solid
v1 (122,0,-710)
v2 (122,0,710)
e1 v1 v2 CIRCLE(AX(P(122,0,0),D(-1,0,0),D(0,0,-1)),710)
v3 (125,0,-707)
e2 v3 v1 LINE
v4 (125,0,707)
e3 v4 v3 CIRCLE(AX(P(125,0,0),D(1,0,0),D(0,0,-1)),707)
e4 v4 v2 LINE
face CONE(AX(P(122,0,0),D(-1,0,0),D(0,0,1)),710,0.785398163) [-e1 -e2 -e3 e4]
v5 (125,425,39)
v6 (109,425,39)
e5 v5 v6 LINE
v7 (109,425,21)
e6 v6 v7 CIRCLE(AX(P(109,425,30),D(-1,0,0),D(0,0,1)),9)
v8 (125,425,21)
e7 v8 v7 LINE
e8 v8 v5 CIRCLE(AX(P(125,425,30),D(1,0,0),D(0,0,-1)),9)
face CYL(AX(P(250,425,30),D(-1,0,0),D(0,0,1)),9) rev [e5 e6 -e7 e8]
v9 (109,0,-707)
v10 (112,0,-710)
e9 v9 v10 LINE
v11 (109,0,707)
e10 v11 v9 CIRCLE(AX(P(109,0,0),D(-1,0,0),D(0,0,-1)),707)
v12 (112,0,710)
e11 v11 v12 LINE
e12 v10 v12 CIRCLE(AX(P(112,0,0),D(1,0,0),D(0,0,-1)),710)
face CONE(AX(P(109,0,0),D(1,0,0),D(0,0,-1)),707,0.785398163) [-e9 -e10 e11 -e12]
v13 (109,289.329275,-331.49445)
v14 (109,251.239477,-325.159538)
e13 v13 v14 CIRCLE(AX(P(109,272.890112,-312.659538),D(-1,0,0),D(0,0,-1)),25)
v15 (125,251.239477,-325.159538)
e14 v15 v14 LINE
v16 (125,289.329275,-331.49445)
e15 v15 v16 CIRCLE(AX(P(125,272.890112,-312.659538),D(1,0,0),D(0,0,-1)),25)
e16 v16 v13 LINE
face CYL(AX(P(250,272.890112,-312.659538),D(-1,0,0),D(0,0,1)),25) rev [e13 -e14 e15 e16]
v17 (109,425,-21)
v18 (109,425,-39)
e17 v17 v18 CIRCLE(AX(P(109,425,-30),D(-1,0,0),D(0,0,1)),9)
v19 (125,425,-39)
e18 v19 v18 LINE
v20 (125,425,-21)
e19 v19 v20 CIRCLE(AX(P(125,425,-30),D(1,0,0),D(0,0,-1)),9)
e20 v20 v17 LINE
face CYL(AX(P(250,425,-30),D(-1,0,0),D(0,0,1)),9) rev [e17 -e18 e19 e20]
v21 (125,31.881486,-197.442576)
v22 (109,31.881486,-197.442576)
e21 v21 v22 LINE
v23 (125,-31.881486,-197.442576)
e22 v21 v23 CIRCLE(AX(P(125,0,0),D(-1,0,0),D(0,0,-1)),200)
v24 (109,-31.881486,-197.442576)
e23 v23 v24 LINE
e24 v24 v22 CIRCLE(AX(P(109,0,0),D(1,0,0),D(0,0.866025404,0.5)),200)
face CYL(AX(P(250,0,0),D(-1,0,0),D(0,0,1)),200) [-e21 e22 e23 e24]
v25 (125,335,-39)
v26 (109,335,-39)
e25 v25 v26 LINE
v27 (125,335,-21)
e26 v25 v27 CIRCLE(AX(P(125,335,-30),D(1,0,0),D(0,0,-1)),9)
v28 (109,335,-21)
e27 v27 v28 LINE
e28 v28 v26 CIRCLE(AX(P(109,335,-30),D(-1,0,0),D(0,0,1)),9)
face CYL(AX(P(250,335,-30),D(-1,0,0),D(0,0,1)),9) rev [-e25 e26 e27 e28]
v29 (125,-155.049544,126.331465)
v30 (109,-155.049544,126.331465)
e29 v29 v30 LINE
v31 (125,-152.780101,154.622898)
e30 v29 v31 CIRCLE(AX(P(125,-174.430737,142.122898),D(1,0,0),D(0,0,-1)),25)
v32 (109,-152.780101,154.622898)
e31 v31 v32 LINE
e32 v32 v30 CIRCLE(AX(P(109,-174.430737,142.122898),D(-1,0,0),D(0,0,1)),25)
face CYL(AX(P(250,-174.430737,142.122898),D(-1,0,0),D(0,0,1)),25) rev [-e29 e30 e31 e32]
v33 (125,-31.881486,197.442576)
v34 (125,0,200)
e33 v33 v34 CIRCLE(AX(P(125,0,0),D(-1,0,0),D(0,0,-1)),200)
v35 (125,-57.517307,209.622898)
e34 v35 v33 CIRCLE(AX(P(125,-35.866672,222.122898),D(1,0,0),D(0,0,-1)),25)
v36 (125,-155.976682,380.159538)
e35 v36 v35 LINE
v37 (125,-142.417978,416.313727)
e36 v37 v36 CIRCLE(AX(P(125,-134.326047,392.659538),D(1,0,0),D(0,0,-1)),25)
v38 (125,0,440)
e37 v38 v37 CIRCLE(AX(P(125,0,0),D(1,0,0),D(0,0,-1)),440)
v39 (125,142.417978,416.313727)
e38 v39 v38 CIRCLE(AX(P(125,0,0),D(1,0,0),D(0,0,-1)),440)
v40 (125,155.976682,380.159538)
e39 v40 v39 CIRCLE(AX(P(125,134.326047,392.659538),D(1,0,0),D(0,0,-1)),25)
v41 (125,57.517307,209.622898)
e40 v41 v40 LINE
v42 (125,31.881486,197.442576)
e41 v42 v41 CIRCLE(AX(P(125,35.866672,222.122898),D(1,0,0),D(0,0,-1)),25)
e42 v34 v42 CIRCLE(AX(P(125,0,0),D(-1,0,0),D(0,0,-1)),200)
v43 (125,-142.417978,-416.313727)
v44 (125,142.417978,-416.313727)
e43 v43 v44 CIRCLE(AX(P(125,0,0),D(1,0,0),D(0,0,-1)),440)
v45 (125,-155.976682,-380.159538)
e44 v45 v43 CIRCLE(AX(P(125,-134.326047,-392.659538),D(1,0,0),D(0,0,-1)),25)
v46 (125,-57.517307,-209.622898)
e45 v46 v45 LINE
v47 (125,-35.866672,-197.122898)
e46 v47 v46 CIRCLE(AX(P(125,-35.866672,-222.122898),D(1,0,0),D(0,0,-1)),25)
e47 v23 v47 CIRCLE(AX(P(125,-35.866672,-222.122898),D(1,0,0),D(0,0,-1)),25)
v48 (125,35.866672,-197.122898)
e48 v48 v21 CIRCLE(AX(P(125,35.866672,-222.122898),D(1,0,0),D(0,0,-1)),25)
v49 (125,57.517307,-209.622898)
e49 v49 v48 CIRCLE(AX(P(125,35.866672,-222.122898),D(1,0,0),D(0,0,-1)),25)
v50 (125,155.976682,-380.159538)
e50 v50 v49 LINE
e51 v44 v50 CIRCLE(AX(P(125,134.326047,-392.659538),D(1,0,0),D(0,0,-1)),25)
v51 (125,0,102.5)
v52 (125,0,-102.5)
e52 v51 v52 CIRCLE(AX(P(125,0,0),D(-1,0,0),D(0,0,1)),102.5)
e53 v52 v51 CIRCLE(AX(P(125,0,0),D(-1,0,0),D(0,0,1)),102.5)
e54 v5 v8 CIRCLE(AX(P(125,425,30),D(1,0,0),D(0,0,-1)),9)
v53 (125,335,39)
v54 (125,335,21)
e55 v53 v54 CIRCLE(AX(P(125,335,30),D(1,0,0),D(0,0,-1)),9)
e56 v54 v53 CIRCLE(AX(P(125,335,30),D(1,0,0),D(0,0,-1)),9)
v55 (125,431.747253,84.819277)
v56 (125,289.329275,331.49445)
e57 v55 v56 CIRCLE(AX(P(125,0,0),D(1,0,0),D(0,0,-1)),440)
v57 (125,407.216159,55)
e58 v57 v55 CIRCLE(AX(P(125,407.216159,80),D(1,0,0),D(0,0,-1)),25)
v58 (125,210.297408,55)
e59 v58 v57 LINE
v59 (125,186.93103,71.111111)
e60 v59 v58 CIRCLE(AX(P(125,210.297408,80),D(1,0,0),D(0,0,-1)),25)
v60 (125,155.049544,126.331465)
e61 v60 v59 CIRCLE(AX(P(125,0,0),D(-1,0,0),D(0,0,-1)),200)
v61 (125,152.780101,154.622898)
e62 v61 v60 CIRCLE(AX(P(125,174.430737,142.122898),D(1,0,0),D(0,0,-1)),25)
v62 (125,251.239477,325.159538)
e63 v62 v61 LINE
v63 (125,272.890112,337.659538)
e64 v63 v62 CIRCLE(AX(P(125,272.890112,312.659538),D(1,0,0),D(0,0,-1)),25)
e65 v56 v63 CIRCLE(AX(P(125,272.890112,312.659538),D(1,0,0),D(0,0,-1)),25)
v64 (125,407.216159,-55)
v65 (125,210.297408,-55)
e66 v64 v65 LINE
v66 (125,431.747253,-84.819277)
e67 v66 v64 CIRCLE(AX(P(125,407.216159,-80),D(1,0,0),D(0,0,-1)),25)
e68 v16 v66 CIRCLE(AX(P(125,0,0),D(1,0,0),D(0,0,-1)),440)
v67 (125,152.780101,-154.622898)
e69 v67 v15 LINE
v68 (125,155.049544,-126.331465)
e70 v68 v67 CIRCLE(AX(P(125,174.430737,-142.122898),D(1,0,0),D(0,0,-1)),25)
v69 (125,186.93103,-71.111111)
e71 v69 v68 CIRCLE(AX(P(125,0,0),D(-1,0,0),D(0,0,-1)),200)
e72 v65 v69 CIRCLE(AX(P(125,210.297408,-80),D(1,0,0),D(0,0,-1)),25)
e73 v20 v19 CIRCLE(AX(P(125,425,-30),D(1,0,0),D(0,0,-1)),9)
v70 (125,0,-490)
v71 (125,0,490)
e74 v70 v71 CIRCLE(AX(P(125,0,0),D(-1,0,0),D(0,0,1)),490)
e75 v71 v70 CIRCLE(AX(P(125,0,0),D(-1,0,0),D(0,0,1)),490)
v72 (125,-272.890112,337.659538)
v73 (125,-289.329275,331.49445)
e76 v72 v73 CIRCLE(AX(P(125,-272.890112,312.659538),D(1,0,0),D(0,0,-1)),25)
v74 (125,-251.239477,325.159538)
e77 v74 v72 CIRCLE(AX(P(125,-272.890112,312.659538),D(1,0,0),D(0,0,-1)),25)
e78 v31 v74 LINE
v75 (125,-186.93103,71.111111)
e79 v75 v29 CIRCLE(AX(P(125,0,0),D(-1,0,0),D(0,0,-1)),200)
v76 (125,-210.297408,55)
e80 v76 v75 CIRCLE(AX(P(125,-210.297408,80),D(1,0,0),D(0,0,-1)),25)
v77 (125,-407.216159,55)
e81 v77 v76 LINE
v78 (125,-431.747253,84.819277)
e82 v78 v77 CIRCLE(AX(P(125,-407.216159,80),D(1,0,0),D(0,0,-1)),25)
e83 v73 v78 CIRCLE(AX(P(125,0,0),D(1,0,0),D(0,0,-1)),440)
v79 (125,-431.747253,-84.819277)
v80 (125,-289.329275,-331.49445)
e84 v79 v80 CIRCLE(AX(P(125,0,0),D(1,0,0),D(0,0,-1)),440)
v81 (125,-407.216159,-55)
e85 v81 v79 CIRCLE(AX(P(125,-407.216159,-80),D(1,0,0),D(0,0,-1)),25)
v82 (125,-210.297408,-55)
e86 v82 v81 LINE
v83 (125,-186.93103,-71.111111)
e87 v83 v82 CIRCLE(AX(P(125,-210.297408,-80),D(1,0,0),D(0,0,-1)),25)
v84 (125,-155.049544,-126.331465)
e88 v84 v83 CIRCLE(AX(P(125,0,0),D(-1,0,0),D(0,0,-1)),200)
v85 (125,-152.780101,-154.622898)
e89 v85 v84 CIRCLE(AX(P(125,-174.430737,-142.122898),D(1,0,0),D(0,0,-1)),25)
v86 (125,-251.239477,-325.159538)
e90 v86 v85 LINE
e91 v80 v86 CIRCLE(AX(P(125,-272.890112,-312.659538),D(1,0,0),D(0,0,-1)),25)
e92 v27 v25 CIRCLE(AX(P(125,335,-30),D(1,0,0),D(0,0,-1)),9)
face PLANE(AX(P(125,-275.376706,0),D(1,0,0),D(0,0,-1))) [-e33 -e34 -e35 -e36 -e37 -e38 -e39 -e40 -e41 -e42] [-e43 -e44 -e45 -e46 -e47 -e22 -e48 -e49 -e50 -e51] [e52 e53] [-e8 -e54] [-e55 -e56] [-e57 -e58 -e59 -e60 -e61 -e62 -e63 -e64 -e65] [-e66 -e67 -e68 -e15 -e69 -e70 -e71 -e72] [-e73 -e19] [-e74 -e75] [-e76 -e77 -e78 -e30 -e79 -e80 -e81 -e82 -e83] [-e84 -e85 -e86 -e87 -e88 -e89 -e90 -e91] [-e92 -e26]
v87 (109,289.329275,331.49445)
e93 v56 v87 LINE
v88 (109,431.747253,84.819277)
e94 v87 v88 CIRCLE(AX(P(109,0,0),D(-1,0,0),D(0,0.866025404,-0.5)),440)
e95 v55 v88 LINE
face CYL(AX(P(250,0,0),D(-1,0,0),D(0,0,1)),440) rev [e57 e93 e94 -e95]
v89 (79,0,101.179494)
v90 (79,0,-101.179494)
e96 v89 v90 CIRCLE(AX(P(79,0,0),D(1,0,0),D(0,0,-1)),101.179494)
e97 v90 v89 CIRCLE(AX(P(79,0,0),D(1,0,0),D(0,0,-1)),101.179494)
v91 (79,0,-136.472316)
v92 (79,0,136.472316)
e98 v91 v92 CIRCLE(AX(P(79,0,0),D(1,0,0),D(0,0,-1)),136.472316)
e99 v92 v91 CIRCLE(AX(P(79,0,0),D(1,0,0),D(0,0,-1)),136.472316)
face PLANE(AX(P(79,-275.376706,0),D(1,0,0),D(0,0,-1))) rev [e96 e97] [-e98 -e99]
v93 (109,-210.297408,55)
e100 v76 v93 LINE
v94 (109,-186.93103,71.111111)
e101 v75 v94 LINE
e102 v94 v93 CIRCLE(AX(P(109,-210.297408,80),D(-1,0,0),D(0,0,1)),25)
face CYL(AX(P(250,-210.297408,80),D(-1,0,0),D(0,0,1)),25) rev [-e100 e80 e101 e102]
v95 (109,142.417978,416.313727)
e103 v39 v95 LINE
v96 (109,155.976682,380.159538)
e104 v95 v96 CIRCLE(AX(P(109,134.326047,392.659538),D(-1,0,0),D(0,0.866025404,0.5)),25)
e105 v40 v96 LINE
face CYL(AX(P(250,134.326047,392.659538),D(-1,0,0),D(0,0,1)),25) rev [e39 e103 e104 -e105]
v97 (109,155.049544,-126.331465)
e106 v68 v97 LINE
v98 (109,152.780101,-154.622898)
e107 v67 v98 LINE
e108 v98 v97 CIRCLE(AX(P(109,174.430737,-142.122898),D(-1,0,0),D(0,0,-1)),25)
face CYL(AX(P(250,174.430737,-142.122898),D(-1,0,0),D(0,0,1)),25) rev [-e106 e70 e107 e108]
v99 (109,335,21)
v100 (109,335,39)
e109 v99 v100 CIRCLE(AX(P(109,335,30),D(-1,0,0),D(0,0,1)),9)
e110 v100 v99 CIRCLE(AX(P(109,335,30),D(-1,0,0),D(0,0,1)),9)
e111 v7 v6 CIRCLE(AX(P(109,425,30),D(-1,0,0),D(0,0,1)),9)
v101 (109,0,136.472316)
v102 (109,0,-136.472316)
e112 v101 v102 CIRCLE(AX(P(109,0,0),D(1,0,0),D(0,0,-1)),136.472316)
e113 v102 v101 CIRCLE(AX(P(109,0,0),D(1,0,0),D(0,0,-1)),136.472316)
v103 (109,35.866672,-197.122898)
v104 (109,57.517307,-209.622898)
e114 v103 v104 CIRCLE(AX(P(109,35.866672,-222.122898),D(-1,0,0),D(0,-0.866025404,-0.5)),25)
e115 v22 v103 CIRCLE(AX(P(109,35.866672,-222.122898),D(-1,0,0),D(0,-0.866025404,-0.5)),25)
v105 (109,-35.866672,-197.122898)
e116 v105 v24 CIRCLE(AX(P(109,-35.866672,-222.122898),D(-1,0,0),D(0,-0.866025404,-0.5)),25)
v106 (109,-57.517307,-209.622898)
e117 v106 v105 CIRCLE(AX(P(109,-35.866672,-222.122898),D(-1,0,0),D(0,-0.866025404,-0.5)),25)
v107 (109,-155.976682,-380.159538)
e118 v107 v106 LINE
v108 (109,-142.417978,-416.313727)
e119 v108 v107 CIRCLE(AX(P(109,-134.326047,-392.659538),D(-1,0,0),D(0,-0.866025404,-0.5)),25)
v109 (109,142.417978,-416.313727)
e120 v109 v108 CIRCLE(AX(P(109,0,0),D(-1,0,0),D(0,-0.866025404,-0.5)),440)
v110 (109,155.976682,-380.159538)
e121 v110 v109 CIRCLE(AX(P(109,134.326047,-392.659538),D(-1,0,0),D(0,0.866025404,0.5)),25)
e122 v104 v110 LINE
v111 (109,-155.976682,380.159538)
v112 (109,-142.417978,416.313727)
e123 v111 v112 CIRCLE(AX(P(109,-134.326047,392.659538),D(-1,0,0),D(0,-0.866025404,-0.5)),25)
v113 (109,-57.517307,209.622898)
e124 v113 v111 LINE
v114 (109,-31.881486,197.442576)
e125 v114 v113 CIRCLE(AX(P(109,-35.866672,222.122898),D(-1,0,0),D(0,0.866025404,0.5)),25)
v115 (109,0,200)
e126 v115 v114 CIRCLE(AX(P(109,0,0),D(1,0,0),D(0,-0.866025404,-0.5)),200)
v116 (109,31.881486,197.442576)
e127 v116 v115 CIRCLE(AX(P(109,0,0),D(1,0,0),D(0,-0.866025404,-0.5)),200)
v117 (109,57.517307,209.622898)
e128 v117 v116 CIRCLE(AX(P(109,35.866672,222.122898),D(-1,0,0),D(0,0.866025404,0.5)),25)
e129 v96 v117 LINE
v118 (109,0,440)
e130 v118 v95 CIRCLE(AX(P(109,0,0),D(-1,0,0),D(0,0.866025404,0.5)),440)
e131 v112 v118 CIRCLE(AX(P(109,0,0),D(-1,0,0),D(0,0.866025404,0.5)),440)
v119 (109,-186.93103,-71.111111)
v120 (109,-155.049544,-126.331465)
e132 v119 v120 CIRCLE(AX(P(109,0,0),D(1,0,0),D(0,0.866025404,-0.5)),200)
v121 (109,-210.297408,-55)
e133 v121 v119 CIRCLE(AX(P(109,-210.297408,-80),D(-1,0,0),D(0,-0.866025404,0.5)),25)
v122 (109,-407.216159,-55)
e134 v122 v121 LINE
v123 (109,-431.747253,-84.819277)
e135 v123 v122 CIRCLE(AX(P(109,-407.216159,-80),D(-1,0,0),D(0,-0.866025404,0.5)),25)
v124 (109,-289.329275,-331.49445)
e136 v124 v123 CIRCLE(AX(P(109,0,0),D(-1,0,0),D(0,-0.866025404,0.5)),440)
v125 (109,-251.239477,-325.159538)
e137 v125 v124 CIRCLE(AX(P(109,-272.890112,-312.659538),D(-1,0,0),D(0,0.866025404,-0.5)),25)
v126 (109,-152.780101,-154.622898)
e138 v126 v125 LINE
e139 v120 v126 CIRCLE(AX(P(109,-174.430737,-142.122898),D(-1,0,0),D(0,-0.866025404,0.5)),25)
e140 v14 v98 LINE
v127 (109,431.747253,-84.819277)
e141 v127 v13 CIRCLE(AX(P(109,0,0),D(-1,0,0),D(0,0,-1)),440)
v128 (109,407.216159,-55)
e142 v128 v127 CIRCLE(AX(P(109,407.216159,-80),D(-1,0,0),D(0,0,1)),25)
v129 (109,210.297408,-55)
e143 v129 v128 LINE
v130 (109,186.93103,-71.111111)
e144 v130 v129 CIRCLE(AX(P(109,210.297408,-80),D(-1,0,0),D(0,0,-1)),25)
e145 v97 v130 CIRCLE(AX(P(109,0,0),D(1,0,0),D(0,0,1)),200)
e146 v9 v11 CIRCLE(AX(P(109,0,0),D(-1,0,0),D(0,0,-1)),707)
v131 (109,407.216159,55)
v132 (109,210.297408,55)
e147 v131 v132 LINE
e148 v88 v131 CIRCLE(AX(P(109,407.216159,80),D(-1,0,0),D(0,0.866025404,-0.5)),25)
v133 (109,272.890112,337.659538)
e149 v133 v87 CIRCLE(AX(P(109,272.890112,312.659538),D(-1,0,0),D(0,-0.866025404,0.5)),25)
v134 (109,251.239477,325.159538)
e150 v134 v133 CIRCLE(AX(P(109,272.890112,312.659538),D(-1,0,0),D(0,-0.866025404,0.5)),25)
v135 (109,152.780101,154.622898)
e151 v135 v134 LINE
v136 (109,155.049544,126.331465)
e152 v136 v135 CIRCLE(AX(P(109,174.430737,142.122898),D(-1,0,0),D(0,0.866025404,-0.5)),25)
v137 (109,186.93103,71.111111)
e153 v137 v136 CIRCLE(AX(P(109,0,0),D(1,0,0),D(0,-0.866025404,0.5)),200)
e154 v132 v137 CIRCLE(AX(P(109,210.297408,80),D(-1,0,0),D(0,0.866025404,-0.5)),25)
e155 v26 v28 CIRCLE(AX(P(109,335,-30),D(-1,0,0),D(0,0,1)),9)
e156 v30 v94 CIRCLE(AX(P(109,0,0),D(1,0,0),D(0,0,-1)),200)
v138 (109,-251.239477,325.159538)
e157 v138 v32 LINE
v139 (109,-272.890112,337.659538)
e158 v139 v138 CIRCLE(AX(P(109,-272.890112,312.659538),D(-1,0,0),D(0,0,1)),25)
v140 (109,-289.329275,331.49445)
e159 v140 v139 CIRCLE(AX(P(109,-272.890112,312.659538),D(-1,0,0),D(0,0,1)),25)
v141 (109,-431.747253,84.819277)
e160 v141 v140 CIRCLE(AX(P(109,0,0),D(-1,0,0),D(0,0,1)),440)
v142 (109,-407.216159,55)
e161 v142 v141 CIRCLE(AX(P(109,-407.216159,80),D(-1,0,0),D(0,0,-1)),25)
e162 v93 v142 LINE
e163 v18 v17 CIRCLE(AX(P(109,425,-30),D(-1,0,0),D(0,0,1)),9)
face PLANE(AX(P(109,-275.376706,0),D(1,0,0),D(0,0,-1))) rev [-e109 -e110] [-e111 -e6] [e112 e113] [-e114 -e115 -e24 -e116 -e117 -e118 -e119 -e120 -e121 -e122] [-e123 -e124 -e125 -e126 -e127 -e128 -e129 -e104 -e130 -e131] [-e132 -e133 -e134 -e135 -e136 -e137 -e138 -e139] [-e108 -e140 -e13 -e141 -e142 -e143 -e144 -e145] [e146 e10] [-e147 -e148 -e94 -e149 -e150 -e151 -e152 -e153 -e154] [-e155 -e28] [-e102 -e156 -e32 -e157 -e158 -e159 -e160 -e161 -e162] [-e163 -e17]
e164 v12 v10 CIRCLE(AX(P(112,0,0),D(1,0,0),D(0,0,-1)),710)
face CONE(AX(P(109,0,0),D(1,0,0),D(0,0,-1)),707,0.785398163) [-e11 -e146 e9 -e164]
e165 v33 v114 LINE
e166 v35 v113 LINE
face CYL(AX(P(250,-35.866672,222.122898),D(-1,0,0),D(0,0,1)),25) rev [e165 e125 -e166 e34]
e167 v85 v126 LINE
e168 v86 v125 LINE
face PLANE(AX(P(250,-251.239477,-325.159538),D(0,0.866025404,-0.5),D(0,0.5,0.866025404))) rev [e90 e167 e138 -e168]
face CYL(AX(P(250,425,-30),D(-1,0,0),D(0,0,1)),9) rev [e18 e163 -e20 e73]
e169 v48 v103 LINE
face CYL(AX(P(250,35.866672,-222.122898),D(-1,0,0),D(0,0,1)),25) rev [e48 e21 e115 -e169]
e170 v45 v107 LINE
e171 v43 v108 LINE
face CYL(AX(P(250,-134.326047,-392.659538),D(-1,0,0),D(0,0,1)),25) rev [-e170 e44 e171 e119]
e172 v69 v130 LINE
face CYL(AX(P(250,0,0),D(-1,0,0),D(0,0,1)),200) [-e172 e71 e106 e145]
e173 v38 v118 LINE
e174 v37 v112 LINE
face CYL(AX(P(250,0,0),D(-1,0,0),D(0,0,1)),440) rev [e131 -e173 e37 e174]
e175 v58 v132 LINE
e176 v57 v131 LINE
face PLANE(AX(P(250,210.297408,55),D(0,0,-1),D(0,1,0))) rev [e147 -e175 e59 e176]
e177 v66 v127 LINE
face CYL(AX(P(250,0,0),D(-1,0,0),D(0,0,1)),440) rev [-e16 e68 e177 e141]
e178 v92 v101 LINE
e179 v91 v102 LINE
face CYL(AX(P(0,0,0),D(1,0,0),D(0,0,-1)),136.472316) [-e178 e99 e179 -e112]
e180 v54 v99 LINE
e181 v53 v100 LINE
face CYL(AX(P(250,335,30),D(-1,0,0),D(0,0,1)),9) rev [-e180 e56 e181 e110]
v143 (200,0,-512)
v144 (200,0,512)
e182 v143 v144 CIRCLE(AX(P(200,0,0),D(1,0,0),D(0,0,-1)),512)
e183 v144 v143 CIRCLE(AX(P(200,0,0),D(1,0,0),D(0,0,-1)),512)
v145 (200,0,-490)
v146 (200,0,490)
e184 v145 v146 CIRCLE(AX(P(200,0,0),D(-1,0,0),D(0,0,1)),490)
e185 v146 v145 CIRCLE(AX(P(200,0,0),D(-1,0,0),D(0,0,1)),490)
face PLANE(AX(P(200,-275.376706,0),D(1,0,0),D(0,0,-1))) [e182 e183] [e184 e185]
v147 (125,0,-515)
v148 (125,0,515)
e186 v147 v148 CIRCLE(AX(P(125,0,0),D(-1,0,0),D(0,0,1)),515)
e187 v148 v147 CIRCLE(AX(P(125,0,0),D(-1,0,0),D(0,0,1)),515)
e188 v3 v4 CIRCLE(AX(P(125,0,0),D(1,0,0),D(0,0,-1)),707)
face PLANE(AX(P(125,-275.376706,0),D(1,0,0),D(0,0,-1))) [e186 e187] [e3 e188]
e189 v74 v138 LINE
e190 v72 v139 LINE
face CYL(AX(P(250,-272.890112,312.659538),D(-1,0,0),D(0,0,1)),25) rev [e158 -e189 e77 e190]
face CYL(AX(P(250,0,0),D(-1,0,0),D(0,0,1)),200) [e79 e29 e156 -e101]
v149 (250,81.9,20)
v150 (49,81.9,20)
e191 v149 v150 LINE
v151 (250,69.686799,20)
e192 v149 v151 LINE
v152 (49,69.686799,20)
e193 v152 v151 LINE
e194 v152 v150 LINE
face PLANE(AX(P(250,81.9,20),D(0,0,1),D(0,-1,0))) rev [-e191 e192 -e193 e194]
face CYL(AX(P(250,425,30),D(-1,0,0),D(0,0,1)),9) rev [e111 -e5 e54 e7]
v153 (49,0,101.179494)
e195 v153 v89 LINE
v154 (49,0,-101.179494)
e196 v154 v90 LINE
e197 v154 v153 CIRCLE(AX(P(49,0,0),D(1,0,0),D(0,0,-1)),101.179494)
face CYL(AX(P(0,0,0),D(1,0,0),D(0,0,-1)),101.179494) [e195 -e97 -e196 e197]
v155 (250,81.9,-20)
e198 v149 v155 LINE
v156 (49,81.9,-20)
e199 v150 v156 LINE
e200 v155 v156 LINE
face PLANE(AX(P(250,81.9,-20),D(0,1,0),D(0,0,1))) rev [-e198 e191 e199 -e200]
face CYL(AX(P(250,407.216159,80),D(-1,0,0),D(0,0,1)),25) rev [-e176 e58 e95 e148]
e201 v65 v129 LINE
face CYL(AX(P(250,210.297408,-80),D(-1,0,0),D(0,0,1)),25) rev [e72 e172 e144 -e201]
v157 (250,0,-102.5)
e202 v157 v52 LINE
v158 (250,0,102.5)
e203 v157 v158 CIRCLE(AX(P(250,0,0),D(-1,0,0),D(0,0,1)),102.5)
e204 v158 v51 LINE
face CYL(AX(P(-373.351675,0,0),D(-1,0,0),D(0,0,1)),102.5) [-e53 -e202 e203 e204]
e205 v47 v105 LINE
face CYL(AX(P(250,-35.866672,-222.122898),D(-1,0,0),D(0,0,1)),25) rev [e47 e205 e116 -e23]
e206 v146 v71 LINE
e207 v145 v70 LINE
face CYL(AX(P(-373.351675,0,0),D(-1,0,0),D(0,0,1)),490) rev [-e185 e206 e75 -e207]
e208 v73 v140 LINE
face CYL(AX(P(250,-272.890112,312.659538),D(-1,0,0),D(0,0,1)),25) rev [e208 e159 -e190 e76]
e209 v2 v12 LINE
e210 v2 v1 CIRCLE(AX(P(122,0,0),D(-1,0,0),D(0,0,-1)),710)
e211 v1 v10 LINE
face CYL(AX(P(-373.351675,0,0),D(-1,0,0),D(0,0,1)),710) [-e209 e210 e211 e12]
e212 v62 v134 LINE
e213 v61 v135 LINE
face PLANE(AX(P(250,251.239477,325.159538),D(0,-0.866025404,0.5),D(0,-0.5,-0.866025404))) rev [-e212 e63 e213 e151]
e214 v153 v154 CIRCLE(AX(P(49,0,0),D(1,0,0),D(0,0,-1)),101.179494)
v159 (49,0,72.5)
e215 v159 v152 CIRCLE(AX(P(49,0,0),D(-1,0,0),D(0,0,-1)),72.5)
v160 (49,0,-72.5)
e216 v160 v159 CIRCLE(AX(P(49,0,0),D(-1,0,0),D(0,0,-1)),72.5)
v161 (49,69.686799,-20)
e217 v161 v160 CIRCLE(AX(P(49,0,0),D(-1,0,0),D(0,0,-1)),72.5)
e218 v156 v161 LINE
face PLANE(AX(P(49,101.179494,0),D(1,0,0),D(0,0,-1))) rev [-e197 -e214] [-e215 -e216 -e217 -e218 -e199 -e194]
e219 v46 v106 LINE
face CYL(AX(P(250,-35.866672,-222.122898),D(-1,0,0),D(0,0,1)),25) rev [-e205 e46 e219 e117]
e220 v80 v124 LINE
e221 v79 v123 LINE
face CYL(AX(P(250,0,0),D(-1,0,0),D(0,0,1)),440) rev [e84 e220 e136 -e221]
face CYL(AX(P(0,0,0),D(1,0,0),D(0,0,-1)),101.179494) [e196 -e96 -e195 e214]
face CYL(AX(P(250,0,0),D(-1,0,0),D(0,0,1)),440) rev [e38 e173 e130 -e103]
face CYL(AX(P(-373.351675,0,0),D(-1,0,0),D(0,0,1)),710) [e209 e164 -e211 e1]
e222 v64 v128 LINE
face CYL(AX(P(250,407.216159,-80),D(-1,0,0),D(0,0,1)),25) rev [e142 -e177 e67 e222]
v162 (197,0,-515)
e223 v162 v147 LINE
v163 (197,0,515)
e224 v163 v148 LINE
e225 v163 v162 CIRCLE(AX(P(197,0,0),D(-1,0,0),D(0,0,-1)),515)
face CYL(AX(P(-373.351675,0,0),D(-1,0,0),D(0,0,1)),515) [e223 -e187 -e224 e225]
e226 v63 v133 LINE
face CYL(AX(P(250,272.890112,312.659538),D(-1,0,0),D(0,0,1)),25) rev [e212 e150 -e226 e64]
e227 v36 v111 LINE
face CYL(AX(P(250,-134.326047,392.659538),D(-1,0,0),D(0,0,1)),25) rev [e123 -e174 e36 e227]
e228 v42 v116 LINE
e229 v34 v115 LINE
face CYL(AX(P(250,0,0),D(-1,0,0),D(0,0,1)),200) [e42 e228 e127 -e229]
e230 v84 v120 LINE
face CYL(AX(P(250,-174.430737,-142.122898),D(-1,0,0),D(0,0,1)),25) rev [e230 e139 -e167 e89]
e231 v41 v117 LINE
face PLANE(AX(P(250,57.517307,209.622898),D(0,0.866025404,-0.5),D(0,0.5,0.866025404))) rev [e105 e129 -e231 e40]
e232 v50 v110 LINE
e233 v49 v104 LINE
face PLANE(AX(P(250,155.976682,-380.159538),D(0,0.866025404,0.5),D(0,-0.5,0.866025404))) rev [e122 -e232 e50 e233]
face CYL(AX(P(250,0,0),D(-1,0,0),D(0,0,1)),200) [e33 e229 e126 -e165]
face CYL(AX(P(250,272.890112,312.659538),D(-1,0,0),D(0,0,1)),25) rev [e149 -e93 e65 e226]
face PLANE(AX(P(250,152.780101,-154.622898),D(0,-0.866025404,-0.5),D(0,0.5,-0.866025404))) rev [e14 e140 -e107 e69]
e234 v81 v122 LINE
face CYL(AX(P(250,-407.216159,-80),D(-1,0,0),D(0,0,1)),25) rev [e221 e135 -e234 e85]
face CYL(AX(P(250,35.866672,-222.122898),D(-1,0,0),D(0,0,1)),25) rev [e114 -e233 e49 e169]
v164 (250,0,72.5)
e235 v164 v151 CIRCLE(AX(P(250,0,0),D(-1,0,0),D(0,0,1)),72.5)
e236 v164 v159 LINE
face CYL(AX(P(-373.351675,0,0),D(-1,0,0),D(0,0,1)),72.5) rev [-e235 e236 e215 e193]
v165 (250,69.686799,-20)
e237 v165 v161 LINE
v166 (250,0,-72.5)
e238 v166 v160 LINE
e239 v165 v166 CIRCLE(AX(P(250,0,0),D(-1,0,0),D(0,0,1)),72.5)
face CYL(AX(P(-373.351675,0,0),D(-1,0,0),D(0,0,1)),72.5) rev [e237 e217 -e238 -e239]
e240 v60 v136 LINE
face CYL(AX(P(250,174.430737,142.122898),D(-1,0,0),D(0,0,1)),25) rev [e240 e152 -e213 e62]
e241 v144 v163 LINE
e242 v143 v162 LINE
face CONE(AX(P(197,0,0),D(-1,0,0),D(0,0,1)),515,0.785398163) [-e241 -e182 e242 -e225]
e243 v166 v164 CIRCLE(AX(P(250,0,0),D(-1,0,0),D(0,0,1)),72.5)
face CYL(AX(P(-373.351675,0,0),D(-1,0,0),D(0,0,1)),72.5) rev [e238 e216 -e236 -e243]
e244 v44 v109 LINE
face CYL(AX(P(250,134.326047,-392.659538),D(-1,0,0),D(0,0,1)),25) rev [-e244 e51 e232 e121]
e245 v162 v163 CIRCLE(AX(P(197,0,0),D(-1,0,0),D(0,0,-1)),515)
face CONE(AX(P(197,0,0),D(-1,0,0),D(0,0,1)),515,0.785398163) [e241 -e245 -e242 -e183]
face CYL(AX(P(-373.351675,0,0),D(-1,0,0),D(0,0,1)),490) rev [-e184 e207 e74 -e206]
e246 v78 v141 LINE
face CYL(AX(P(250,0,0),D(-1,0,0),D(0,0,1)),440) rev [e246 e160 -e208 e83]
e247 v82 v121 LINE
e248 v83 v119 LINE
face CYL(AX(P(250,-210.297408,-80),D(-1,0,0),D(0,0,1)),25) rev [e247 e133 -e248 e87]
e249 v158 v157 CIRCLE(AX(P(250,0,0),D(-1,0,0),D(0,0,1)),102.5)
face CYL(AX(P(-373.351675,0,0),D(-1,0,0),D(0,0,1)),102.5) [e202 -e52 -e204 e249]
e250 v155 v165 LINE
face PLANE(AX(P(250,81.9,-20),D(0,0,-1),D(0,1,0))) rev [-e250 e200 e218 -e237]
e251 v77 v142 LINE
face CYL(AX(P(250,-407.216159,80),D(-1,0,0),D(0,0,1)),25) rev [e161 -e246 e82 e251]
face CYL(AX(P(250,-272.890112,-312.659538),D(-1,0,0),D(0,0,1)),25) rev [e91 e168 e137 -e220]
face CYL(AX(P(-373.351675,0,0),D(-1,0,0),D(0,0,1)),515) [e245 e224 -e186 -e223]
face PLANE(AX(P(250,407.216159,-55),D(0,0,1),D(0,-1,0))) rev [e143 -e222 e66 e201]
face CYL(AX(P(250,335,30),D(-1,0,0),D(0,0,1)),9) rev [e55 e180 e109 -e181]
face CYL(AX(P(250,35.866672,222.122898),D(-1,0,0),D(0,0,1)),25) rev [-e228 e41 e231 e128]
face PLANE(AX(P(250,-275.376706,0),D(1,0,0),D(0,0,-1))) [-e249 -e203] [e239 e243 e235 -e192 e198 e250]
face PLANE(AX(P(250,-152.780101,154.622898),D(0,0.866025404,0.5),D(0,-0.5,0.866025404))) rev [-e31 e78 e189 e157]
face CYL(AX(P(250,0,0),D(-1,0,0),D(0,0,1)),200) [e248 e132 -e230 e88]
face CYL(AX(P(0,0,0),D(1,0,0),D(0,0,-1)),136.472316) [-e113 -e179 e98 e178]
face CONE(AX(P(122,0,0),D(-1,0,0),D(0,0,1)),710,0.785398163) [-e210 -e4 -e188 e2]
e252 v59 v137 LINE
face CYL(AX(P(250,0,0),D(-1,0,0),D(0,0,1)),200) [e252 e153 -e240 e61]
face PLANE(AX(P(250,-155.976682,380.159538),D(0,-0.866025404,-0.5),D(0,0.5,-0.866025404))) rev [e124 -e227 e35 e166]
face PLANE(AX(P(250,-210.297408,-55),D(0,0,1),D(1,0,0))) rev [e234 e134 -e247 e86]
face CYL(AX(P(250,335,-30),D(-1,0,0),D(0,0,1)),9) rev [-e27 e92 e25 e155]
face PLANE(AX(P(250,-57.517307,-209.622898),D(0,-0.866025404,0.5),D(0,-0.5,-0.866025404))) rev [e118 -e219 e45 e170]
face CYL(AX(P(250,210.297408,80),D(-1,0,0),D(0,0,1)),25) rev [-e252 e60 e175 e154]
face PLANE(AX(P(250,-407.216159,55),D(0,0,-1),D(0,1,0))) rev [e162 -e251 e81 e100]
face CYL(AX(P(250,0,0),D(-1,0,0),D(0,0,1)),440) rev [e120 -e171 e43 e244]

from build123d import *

# Parameters (mm, degrees)
CUT_EXTRUDE1_DEPTH       = 1014.9432923
CIRPATTERN1_COUNT        = 6
BOSS_EXTRUDE1_REACH      = 1015.943
FILLET2_R                = 10
CIRPATTERN2_COUNT        = 6
FILLET2_OF_CIRPATTERN2_R = 10
SKETCH5_R                = 9
CUT_EXTRUDE2_DEPTH       = 1014.9432923
CUT_EXTRUDE3_DEPTH       = 20
CUT_EXTRUDE3_DEPTH_BACK  = 1041.251892572
CHAMFER1_SIZE            = 3
SKETCH7_W                = 40
SKETCH7_H                = 18.8
CUT_EXTRUDE4_DEPTH       = 1035.746345729


with BuildPart() as part:
    # Sketch1 → Revolve1 (revolve)
    with BuildSketch(Plane.XY, mode=Mode.PRIVATE) as revolve1_sk:
        Polygon((0, 102.5), (79, 102.5), (79, 137.5), (109, 137.5), (109, 534), (-31, 534), (-31, 550), (109, 550), (109, 710), (125, 710), (125, 515), (200, 515), (200, 490), (125, 490), (125, 102.5), (250, 102.5), (250, 72.5), (0, 72.5), align=None)
    revolve(revolve1_sk.sketch.rotate(Axis((-373.351674541, 0, 0), (1, 0, 0)), 90), axis=Axis((-373.351674541, 0, 0), (1, 0, 0)))

    # Sketch3 → Cut-Extrude1 (cut, through all)
    with BuildSketch(Plane.ZY.offset(-109)):
        with BuildLine():
            Line((-55, 407.216158815), (-55, 210.297408448))
            ThreePointArc((-55, 210.297408448), (-59.418184941, 196.106253143), (-71.111111111, 186.931029732))
            ThreePointArc((-71.111111111, 186.931029732), (-100, 173.205080757), (-126.331464948, 155.049543579))
            ThreePointArc((-126.331464948, 155.049543579), (-140.123904592, 149.510784178), (-154.622898066, 152.780101432))
            Line((-154.622898066, 152.780101432), (-325.159538365, 251.239476616))
            ThreePointArc((-325.159538365, 251.239476616), (-337.320790629, 268.78857093), (-331.494450315, 289.329275066))
            ThreePointArc((-331.494450315, 289.329275066), (-220, 381.051177665), (-84.819277108, 431.747252719))
            ThreePointArc((-84.819277108, 431.747252719), (-64.117335358, 426.522659374), (-55, 407.216158815))
        make_face()
    cut_extrude1 = extrude(amount=-CUT_EXTRUDE1_DEPTH, mode=Mode.SUBTRACT)

    # CirPattern1: Cut-Extrude1 ×6 about axis
    cirpattern1_axis = Axis((0, 0, 0), (1, 0, 0))
    for i in range(1, CIRPATTERN1_COUNT):
        add(cut_extrude1.rotate(cirpattern1_axis, i * 360 / CIRPATTERN1_COUNT), mode=Mode.SUBTRACT)

    # Boss-Extrude1: up to this face of the body (flat: up to its plane)
    boss_extrude1_end = Plane(part.part.faces().sort_by_distance((0, 0, -75.399137803))[0])
    # Sketch4 → Boss-Extrude1 (add, up to the picked face)
    with BuildSketch(Plane.ZY.offset(-109), mode=Mode.PRIVATE) as boss_extrude1_sk1:
        with BuildLine():
            Line((-8, 533.940071544), (-8, 102.187327982))
            ThreePointArc((-8, 102.187327982), (0, 102.5), (8, 102.187327982))
            Line((8, 102.187327982), (8, 533.940071544))
            ThreePointArc((8, 533.940071544), (0, 534), (-8, 533.940071544))
        make_face()
    boss_extrude1_tool1 = split(extrude(boss_extrude1_sk1.sketch, amount=BOSS_EXTRUDE1_REACH, mode=Mode.PRIVATE), bisect_by=boss_extrude1_end, keep=Keep.BOTH, mode=Mode.PRIVATE)
    boss_extrude1 = boss_extrude1_tool1.solids().sort_by(Axis((109, 318.187922, 0), (-1, 0, 0)))[0]
    add(boss_extrude1)

    # Fillet2
    fillet2_edges = [part.edges().sort_by_distance(p)[0] for p in [
        (94, 137.267075441, 8),
        (39.5, 102.187327982, -8),
        (94, 137.267075441, -8),
        (109, 335.603573492, 8),
        (39.5, 102.187327982, 8),
        (54.5, 533.940071544, -8),
        (109, 335.603573492, -8),
        (54.5, 533.940071544, 8),
    ]]
    fillet(fillet2_edges, radius=FILLET2_R)

    # CirPattern2: Boss-Extrude1 ×6 about axis
    cirpattern2_axis = Axis((0, 0, 0), (1, 0, 0))
    for i in range(1, CIRPATTERN2_COUNT):
        add(boss_extrude1.rotate(cirpattern2_axis, i * 360 / CIRPATTERN2_COUNT))

    # Fillet2 of CirPattern2
    fillet2_of_cirpattern2_edges = [part.edges().sort_by_distance(p)[0] for p in [
        (94, 61.70533449, 122.876774435),
        (39.5, 58.021867221, 84.496821977),
        (94, 75.561740951, 114.876774435),
        (109, 160.873583516, 294.641220245),
        (39.5, 44.16546076, 92.496821977),
        (54.5, 273.898239002, 458.405666055),
        (109, 174.729989976, 286.641220245),
        (54.5, 260.041832542, 466.405666055),
        (94, -75.561740951, 114.876774435),
        (39.5, -44.16546076, 92.496821977),
        (94, -61.70533449, 122.876774435),
        (109, -174.729989976, 286.641220245),
        (39.5, -58.021867221, 84.496821977),
        (54.5, -260.041832542, 466.405666055),
        (109, -160.873583516, 294.641220245),
        (54.5, -273.898239002, 458.405666055),
        (94, -137.267075441, -8),
        (39.5, -102.187327982, 8),
        (94, -137.267075441, 8),
        (109, -335.603573492, -8),
        (39.5, -102.187327982, -8),
        (54.5, -533.940071544, 8),
        (109, -335.603573492, 8),
        (54.5, -533.940071544, -8),
        (94, -61.70533449, -122.876774435),
        (39.5, -58.021867221, -84.496821977),
        (94, -75.561740951, -114.876774435),
        (109, -160.873583516, -294.641220245),
        (39.5, -44.16546076, -92.496821977),
        (54.5, -273.898239002, -458.405666055),
        (109, -174.729989976, -286.641220245),
        (54.5, -260.041832542, -466.405666055),
        (94, 75.561740951, -114.876774435),
        (39.5, 44.16546076, -92.496821977),
        (94, 61.70533449, -122.876774435),
        (109, 174.729989976, -286.641220245),
        (39.5, 58.021867221, -84.496821977),
        (54.5, 260.041832542, -466.405666055),
        (109, 160.873583516, -294.641220245),
        (54.5, 273.898239002, -458.405666055),
    ]]
    fillet(fillet2_of_cirpattern2_edges, radius=FILLET2_OF_CIRPATTERN2_R)

    # Sketch5 → Cut-Extrude2 (cut, through all)
    with BuildSketch(Plane.ZY.offset(-109)):
        with Locations((-30, 425)):
            Circle(SKETCH5_R)
        with Locations((-30, 335)):
            Circle(SKETCH5_R)
        with Locations((30, 335)):
            Circle(SKETCH5_R)
        with Locations((30, 425)):
            Circle(SKETCH5_R)
    extrude(amount=-CUT_EXTRUDE2_DEPTH, mode=Mode.SUBTRACT)

    # Sketch6 → Cut-Extrude3 (cut, two sides: drawn at the far end of the back side and taken through both)
    with BuildSketch(Plane.XY.offset(8).offset(-CUT_EXTRUDE3_DEPTH_BACK)):
        with BuildLine():
            Line((94, 395), (109, 395))
            Line((109, 395), (109, 365))
            Line((109, 365), (94, 365))
            ThreePointArc((94, 365), (79, 380), (94, 395))
        make_face()
    extrude(amount=CUT_EXTRUDE3_DEPTH + CUT_EXTRUDE3_DEPTH_BACK, mode=Mode.SUBTRACT)

    # Chamfer1
    chamfer1_edges = [part.edges().sort_by_distance(p)[0] for p in [
        (-31, 0, -550),
        (109, 0, -710),
        (125, 0, -710),
        (200, 0, -515),
    ]]
    chamfer(chamfer1_edges, length=CHAMFER1_SIZE)

    # Sketch7 → Cut-Extrude4 (cut, through all)
    with BuildSketch(Plane.ZY):
        with Locations((0, 72.5)):
            Rectangle(SKETCH7_W, SKETCH7_H)
    extrude(amount=-CUT_EXTRUDE4_DEPTH, mode=Mode.SUBTRACT)

    # Sketch8 → Cut-Revolve1 (revolve, cut)
    with BuildSketch(Plane.XY, mode=Mode.PRIVATE) as cut_revolve1_sk:
        Polygon((109, 550), (-31, 550), (-31, 146.397575117), (-31, 0), (49, 0), (49, 101.17949397), (79, 101.17949397), (79, 136.472315787), (109, 136.472315787), align=None)
    revolve(cut_revolve1_sk.sketch.rotate(Axis((0, 0, 0), (-1, 0, 0)), 90), axis=Axis((0, 0, 0), (-1, 0, 0)), mode=Mode.SUBTRACT)


solid = part.part
